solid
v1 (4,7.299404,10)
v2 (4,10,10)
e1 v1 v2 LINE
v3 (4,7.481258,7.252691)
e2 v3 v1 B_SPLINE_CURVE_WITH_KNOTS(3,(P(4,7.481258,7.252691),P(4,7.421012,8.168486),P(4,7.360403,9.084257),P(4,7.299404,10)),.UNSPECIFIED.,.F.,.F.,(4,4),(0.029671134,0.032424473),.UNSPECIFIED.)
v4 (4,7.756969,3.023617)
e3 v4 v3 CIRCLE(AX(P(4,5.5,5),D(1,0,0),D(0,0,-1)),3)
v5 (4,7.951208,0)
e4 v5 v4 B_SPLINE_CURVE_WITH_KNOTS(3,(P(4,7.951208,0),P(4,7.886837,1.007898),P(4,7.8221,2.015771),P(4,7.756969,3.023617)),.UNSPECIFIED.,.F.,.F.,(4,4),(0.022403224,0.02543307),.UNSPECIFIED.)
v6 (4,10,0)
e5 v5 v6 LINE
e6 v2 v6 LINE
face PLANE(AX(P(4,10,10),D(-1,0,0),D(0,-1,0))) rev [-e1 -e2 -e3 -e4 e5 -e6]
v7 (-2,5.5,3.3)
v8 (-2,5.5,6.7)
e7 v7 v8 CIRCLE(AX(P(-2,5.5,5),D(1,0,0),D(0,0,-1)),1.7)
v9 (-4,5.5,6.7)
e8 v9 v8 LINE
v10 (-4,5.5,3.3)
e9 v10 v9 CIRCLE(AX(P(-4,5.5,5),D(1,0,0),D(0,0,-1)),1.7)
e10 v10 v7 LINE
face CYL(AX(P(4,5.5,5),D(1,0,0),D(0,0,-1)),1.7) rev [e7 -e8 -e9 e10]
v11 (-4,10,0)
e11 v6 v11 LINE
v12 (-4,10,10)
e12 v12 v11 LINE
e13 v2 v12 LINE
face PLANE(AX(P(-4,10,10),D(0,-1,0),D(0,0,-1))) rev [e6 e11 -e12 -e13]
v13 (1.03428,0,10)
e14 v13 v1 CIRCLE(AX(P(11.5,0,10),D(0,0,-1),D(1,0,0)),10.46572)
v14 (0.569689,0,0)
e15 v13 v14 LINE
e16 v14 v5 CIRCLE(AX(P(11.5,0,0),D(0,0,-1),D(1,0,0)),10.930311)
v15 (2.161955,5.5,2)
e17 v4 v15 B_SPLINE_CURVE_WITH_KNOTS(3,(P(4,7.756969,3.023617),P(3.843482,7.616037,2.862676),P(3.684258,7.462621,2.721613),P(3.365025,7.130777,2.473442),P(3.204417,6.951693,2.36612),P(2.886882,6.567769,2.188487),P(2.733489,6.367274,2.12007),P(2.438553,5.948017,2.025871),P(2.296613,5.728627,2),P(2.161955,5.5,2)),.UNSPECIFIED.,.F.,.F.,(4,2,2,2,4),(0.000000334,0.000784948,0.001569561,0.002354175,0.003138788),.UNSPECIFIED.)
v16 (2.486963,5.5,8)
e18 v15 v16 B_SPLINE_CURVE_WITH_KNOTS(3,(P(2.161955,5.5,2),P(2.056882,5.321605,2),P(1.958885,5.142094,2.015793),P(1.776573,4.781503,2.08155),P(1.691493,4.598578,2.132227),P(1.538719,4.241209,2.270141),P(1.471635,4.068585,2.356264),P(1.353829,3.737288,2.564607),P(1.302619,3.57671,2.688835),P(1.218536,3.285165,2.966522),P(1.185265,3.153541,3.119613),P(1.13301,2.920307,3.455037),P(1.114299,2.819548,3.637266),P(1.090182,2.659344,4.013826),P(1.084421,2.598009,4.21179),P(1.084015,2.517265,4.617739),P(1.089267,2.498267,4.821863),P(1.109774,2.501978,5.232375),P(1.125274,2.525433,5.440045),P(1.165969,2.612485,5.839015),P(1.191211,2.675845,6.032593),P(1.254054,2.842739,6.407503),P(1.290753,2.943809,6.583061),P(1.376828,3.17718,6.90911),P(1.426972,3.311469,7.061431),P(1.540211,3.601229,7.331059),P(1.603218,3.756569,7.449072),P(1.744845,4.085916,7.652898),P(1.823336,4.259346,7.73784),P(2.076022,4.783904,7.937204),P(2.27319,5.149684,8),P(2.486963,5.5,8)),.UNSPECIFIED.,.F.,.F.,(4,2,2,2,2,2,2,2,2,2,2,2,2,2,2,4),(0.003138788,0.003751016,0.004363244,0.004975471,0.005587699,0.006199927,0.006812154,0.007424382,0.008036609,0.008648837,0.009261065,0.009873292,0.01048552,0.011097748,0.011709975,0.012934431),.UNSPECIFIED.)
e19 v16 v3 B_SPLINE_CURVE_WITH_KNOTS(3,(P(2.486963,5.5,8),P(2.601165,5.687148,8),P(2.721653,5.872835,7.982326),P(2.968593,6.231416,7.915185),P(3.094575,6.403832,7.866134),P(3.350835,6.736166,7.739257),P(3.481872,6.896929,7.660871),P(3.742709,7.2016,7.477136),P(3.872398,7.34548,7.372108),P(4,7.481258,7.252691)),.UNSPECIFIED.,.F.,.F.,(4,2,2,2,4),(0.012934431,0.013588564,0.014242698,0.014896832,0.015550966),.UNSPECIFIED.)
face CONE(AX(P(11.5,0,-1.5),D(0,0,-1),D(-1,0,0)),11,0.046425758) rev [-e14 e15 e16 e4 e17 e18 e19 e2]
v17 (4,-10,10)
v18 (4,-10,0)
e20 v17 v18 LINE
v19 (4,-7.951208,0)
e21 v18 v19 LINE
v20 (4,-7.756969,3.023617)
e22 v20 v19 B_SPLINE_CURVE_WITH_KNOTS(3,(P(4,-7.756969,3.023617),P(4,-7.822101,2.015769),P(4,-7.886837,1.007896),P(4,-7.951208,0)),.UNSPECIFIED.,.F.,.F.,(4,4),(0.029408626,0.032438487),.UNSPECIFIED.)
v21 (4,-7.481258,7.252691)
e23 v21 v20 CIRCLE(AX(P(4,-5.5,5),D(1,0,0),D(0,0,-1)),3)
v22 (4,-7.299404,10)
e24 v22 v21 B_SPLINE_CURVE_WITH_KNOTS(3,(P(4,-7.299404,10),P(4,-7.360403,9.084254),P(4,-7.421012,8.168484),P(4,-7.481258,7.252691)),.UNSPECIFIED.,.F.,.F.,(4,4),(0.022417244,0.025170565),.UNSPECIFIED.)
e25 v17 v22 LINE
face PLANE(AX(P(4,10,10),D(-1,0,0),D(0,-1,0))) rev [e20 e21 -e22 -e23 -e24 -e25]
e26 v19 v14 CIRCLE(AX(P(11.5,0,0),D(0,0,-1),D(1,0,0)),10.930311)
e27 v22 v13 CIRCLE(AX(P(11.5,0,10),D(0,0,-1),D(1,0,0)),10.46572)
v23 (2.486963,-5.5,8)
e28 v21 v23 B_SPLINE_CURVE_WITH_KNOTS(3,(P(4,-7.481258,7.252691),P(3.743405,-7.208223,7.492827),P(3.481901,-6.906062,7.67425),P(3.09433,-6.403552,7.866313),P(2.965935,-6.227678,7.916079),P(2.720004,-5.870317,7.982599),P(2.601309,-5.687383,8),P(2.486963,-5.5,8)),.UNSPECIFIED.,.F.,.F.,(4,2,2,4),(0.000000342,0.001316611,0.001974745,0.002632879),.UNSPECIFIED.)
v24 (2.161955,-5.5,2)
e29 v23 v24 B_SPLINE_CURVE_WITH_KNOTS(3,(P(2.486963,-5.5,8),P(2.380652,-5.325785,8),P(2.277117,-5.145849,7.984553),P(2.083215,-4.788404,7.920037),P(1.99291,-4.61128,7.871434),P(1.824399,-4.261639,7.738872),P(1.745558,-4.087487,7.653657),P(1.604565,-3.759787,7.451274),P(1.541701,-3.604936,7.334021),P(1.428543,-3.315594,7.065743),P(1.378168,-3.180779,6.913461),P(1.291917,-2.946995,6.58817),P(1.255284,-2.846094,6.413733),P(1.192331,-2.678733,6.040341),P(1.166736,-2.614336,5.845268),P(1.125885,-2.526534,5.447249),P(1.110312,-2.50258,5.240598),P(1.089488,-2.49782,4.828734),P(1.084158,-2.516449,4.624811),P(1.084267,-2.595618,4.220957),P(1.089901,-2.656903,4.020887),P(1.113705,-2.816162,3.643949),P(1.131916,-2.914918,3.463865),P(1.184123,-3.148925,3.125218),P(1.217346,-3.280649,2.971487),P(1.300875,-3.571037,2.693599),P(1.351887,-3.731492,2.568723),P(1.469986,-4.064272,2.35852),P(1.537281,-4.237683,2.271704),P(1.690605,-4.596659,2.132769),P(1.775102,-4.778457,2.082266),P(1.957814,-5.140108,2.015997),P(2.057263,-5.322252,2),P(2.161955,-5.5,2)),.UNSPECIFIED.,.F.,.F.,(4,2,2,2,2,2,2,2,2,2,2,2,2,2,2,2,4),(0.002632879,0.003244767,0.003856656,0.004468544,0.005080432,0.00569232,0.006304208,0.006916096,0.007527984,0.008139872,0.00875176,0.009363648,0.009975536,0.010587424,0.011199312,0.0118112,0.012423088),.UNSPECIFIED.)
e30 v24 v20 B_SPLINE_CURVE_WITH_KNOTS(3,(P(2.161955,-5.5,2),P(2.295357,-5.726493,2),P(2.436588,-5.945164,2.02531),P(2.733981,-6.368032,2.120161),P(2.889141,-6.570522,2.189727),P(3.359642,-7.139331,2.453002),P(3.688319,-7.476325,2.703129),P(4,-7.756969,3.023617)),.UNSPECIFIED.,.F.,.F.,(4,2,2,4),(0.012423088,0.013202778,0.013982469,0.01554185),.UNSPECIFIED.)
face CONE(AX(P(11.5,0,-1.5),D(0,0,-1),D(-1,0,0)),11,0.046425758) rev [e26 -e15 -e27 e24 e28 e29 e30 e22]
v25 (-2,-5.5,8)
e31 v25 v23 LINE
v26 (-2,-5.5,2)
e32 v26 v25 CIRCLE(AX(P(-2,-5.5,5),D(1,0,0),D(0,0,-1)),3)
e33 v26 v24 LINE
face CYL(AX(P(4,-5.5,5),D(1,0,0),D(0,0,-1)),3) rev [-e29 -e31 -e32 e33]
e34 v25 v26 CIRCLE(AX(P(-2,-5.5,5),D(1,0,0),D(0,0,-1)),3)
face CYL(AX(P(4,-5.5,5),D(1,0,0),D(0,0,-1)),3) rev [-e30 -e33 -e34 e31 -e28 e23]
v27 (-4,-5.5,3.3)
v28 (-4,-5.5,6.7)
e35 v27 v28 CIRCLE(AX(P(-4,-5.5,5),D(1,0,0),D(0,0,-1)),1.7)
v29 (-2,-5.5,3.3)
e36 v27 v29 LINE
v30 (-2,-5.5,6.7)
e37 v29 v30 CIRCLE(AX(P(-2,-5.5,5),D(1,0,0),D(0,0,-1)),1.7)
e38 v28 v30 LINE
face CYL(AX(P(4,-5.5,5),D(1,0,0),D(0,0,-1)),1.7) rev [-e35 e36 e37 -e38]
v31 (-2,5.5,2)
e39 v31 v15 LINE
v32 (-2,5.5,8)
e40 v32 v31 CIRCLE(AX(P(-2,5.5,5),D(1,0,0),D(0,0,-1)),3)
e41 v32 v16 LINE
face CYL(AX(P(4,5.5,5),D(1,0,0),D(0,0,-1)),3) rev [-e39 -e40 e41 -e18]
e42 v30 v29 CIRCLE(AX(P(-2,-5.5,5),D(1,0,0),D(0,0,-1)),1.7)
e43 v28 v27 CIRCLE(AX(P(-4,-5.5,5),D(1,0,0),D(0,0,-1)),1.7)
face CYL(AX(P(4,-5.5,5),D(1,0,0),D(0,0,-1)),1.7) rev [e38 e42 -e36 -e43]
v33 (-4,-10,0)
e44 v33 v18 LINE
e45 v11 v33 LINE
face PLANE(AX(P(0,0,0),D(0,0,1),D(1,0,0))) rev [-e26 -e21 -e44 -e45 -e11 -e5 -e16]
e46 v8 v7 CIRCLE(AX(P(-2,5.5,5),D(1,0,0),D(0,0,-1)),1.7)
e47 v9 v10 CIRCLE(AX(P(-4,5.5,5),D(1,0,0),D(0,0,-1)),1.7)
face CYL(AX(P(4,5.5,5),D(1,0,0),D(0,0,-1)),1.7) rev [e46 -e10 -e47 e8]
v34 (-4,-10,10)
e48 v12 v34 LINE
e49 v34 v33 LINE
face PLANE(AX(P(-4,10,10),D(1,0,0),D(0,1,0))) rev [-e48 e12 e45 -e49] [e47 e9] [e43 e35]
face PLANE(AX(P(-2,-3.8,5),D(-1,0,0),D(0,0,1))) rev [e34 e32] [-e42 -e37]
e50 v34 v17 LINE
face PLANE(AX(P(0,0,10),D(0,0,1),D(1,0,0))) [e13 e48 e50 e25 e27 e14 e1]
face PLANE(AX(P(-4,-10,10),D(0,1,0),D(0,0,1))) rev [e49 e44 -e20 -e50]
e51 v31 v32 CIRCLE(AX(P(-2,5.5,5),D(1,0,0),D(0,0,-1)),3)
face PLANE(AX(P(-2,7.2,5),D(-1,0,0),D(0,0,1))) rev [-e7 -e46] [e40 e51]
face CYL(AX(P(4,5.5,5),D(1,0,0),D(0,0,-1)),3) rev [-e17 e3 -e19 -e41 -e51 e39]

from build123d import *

# Parameters (mm, degrees)
SKETCH_1_W                   = 8
SKETCH_1_H                   = 20
EXTRUDE_1_DEPTH              = 10
HOLE_WIZARD_M3_1_D           = 3.4
HOLE_WIZARD_M3_1_CBORE_D     = 6
HOLE_WIZARD_M3_1_CBORE_DEPTH = 6


with BuildPart() as part:
    # 草图1 → 凸台-拉伸1 (new body)
    with BuildSketch(Plane.XY):
        Rectangle(SKETCH_1_W, SKETCH_1_H)
    extrude(amount=EXTRUDE_1_DEPTH)

    # M3 六角圆柱头螺钉的柱形沉头孔1 (through all)
    with Locations(Plane(origin=(4, 0, 0), x_dir=(0, 0, -1), z_dir=(1, 0, 0))):
        with Locations((-5, 5.5), (-5, -5.5)):
            CounterBoreHole(HOLE_WIZARD_M3_1_D / 2, HOLE_WIZARD_M3_1_CBORE_D / 2, HOLE_WIZARD_M3_1_CBORE_DEPTH)

    # 草图4 → 切除-旋转1 (revolve, cut)
    with BuildSketch(Plane(origin=(0, 0, 0), x_dir=(1, 0, 0), z_dir=(0, 1, 0))):
        Polygon((11.5, 1.5), (0.5, 1.5), (1.200682375, -13.581690109), (11.5, -13.581690109), align=None)
    revolve(axis=Axis((11.5, 0, 13.581690109), (0, 0, -1)), mode=Mode.SUBTRACT)


solid = part.part
